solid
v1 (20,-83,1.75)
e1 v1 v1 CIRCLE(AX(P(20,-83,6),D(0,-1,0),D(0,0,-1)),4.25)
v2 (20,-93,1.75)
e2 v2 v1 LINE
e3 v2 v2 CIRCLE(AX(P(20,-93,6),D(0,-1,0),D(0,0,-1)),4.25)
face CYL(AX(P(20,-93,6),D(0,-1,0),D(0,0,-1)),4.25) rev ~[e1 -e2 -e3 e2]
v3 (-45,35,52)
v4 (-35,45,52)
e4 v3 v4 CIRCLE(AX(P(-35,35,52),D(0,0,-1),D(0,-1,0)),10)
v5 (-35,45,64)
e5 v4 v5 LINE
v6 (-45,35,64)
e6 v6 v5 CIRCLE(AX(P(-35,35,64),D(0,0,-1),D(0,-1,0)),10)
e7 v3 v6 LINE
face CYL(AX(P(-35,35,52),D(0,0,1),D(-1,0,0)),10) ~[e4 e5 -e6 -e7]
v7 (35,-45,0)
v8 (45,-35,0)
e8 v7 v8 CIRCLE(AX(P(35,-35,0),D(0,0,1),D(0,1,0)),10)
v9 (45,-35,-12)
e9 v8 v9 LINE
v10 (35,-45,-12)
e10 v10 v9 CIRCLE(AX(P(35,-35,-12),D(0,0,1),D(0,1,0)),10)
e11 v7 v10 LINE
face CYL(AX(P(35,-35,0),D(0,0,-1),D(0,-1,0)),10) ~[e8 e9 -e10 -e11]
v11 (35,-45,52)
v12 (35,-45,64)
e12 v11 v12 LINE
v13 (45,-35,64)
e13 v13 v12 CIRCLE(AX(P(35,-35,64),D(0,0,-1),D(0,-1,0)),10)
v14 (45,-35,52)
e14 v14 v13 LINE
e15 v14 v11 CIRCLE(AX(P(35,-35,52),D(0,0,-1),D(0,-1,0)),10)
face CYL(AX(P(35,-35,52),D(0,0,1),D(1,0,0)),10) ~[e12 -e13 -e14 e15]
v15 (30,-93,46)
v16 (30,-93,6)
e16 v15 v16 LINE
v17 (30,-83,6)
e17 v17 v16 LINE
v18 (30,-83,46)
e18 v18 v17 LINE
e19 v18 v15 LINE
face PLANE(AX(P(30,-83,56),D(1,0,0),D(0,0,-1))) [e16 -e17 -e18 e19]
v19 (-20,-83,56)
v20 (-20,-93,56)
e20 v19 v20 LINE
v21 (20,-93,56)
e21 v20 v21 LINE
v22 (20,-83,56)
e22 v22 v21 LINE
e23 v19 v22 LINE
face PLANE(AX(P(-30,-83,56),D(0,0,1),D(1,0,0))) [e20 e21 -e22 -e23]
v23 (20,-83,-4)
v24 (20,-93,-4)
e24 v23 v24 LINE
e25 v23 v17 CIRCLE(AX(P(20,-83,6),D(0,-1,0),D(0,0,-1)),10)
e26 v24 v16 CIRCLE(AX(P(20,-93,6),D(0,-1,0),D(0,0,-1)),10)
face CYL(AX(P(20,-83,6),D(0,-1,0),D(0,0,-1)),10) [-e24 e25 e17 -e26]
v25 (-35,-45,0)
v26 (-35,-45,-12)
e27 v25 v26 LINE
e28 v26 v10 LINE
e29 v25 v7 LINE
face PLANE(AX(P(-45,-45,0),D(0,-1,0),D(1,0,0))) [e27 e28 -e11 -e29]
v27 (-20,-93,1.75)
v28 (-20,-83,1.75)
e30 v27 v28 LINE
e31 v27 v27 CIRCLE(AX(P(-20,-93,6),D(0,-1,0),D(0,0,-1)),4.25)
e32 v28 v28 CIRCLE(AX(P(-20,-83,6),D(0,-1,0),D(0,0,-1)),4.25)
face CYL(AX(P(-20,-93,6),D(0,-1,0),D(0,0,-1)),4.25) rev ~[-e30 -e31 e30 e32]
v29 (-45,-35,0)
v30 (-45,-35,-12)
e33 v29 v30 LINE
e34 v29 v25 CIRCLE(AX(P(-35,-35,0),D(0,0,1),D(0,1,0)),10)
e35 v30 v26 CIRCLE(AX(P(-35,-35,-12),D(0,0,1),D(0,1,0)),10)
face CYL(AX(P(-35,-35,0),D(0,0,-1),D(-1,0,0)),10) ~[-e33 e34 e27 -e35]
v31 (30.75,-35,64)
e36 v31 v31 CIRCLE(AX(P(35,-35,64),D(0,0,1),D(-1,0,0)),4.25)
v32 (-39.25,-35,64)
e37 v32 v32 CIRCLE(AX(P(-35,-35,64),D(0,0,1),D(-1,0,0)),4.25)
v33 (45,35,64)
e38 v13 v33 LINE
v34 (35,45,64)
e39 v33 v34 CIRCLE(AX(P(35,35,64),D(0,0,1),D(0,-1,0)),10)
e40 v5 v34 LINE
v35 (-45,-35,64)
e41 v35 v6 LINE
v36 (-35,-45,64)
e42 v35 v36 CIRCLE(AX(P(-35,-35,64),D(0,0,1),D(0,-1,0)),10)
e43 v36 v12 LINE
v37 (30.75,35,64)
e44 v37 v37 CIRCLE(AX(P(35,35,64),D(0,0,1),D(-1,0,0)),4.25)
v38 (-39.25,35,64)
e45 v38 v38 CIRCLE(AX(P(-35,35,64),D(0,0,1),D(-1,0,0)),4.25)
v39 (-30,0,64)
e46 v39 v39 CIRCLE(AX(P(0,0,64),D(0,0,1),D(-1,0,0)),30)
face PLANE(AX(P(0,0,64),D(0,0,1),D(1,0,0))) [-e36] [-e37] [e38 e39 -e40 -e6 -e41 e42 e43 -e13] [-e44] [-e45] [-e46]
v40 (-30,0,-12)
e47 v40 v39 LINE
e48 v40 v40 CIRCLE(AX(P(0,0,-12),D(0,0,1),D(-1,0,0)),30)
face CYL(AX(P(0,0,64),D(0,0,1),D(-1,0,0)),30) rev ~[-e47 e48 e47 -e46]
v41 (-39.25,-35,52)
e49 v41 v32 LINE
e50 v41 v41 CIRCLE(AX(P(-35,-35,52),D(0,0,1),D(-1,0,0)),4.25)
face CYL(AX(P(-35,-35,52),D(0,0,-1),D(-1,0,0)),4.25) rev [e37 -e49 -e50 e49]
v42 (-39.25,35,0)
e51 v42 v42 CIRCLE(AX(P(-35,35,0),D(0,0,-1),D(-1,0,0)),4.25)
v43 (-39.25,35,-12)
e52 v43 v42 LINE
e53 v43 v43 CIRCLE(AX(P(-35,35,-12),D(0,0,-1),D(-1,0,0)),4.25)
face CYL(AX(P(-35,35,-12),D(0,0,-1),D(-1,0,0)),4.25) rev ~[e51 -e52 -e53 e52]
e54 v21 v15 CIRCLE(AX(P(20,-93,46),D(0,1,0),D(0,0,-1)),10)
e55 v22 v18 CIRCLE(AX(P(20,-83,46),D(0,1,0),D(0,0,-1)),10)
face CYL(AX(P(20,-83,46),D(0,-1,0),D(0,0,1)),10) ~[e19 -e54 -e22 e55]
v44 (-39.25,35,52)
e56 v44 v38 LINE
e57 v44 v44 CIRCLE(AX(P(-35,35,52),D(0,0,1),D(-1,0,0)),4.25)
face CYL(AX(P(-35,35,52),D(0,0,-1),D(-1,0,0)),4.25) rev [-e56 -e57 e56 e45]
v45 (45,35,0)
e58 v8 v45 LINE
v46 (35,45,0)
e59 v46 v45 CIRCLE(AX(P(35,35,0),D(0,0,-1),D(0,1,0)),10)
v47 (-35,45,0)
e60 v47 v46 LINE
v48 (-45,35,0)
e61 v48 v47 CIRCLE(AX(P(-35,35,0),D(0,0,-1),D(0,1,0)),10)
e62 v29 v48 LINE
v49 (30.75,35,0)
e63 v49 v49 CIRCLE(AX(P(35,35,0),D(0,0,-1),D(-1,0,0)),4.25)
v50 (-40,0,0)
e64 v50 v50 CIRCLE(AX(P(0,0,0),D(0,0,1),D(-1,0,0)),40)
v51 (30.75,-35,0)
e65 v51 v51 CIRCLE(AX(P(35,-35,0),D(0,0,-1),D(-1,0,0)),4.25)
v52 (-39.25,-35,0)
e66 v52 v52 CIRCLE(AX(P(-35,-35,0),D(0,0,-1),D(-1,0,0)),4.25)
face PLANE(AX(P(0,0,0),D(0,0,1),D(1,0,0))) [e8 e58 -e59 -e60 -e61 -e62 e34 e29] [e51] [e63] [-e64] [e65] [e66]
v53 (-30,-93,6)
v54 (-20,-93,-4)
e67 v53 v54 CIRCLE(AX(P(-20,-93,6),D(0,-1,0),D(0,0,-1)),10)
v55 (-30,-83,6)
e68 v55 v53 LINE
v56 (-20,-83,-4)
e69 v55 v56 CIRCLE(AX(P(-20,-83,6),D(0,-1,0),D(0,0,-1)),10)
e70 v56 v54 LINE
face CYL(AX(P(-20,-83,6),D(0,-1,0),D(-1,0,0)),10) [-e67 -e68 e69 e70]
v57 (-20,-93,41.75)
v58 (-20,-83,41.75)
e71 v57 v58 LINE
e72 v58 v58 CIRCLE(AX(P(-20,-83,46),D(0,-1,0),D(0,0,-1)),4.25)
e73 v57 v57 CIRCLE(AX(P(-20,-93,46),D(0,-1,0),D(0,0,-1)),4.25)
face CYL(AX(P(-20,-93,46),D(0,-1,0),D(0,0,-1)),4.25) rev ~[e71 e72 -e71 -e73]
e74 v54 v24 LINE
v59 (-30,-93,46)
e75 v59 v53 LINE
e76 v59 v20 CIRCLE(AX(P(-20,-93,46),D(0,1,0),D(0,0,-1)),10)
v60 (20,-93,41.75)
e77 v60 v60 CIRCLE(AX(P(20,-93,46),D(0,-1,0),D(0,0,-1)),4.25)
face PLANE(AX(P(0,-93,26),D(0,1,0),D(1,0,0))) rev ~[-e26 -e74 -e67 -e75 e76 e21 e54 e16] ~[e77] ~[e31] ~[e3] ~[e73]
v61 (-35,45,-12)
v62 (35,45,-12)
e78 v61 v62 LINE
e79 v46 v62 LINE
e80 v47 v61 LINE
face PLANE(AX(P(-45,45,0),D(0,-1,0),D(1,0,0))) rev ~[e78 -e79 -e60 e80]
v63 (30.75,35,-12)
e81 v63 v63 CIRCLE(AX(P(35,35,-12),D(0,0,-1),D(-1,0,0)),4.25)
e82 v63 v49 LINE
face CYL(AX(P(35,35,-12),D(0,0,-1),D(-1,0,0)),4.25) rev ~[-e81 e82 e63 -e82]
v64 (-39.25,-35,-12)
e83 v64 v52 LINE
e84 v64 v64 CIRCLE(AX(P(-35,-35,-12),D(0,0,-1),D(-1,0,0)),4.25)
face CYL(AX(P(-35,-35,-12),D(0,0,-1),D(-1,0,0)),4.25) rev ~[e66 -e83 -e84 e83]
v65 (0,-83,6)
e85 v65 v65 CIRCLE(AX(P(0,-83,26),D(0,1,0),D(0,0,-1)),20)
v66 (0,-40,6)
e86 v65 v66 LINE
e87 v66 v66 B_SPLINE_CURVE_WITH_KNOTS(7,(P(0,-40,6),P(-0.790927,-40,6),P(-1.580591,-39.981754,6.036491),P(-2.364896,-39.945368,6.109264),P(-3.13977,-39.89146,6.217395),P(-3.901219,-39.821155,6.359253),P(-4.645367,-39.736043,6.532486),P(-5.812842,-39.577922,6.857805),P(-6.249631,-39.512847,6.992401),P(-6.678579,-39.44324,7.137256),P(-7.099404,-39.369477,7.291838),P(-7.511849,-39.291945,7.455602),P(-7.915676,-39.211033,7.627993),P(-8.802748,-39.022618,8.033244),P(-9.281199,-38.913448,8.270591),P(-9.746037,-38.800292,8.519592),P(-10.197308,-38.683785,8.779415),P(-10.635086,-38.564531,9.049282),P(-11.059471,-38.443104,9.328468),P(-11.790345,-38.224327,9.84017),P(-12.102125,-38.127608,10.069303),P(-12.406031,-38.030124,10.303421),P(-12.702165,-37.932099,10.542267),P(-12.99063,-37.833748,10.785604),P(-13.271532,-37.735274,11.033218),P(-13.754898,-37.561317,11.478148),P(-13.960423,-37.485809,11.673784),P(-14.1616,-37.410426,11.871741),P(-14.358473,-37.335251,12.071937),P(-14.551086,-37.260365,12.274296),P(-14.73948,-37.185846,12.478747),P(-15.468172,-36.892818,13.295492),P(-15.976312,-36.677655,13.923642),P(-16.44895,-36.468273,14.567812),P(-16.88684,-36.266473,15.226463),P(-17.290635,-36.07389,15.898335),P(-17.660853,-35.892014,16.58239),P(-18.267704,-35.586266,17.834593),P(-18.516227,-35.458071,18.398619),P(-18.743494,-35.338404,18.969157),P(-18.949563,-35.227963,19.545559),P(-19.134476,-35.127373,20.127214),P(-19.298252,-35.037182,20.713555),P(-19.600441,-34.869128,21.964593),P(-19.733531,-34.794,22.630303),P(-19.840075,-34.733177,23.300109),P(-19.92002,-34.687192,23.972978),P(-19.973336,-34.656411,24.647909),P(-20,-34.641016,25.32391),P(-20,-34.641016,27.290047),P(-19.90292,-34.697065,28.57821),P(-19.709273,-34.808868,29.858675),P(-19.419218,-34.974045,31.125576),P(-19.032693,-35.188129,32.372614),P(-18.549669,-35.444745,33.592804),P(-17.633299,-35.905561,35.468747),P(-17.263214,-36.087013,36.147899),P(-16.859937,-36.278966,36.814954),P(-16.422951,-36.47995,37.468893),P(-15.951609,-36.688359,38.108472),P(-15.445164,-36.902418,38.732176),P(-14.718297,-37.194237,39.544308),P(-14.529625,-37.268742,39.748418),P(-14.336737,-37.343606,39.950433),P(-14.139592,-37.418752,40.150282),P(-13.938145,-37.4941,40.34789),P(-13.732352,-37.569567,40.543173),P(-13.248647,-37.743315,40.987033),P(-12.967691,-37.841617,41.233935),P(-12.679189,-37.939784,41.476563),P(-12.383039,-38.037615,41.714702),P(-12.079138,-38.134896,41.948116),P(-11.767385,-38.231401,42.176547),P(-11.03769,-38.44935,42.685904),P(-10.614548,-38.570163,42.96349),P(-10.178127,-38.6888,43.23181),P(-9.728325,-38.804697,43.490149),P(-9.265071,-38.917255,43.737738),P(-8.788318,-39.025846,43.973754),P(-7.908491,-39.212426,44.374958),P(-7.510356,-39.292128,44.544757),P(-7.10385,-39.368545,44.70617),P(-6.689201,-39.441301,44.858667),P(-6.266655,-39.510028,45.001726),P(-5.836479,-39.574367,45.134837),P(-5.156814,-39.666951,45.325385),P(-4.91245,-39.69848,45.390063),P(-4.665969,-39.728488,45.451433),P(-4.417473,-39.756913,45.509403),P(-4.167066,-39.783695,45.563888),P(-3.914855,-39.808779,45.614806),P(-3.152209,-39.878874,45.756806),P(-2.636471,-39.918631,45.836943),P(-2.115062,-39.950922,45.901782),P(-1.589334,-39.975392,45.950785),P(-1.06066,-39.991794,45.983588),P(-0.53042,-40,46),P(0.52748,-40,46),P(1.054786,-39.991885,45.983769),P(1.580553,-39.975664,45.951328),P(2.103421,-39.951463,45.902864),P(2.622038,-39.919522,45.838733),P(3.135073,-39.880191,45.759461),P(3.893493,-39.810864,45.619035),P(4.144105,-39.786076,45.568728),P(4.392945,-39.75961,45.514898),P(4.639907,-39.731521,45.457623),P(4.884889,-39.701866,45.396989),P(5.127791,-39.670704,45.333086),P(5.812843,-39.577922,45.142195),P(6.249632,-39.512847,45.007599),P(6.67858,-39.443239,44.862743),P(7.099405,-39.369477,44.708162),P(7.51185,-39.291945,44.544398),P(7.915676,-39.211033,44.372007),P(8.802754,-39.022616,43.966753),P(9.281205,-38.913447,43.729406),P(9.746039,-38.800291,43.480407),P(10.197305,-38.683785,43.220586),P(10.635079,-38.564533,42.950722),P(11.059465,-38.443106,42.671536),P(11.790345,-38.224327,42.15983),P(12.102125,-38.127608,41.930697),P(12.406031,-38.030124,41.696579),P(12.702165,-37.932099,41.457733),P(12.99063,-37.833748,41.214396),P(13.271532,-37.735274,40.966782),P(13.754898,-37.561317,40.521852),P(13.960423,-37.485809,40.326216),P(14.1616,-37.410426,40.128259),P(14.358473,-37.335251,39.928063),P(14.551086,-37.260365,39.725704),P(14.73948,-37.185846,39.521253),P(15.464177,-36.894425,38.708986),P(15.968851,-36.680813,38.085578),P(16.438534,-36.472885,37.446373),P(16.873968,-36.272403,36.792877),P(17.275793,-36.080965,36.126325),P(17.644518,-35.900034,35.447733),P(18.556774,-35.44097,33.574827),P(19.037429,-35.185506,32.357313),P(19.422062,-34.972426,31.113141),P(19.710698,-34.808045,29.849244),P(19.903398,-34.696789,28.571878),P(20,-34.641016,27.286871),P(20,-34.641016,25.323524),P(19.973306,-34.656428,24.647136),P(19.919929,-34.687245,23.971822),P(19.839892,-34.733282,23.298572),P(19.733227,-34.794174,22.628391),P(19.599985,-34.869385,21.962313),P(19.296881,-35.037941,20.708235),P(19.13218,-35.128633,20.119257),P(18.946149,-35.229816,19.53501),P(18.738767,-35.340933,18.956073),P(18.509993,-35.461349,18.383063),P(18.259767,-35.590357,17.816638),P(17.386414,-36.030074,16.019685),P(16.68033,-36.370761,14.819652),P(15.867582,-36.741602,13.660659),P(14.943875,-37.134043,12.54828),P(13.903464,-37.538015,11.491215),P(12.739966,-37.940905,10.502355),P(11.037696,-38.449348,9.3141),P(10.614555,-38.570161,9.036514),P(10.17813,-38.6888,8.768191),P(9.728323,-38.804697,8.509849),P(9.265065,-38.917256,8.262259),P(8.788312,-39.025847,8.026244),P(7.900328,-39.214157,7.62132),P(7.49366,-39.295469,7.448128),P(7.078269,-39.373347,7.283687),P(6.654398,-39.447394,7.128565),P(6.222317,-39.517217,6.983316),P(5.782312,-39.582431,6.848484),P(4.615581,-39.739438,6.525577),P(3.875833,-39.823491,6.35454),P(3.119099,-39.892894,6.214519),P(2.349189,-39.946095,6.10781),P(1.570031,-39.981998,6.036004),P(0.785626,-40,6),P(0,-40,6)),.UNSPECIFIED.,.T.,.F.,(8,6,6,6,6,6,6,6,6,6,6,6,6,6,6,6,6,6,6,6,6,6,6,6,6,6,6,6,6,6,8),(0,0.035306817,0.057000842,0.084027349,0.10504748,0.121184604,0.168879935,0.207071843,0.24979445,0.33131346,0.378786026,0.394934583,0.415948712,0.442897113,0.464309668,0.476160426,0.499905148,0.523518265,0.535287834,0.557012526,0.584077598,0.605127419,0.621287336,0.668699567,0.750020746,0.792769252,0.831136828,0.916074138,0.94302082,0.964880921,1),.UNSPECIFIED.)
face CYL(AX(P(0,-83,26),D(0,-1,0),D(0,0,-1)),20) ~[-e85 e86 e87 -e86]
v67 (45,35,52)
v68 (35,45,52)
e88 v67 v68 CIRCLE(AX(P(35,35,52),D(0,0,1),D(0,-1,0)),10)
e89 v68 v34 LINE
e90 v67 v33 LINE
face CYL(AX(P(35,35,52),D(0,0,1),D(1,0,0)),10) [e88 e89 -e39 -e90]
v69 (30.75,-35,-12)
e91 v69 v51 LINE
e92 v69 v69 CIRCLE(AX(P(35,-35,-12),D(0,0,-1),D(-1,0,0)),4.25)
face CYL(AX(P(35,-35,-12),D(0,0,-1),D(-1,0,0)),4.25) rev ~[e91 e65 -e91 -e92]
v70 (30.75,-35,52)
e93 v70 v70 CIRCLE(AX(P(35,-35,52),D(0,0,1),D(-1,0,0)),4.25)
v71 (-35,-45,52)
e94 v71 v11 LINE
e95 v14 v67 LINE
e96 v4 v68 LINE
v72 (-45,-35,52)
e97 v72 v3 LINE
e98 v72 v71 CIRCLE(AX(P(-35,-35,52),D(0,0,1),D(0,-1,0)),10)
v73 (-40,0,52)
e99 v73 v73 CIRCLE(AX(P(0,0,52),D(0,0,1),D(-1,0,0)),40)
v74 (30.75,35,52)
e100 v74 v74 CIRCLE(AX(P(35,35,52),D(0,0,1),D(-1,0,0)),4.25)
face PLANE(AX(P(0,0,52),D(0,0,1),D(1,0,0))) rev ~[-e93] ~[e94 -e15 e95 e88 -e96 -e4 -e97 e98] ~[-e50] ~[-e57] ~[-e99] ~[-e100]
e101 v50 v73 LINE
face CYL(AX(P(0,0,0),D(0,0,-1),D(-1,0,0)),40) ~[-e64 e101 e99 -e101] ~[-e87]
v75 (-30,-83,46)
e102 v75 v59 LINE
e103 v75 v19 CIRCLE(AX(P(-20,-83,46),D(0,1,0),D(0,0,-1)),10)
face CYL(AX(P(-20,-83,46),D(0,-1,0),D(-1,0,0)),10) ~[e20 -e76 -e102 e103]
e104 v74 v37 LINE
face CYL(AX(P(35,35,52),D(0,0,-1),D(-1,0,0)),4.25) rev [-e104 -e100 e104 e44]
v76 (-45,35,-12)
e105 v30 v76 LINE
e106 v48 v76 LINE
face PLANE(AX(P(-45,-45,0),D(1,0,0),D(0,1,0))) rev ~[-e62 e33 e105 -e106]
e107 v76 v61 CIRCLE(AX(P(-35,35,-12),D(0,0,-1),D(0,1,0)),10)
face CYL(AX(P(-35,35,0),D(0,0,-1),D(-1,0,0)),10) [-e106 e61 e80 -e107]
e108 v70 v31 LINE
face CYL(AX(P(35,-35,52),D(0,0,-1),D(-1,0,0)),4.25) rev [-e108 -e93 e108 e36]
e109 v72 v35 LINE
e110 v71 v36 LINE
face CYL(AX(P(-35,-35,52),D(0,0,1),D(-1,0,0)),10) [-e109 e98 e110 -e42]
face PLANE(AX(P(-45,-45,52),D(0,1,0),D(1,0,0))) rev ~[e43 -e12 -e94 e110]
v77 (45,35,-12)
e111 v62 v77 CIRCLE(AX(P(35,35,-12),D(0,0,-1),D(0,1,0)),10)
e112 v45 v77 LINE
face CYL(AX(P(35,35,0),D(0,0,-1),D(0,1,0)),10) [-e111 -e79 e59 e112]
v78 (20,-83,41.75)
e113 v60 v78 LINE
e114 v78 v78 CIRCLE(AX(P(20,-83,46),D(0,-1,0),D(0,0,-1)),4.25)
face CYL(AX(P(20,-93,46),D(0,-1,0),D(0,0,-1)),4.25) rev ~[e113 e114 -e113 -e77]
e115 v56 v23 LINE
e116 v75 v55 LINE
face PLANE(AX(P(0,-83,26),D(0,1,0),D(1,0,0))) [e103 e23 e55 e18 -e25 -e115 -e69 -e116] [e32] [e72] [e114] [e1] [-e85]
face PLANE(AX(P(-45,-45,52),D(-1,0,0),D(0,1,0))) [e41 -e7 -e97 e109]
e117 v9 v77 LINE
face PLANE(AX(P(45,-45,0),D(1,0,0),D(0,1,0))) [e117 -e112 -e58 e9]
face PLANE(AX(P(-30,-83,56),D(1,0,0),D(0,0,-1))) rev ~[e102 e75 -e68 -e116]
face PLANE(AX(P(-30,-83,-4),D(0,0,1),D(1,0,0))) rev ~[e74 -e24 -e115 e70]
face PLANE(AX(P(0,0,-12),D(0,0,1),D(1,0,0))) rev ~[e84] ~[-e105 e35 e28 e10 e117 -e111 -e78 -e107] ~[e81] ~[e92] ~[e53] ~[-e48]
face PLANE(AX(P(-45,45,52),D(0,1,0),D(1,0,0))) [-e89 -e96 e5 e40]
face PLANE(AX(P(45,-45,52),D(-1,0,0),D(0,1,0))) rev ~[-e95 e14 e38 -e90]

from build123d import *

# Parameters (mm, degrees)
BODY_TUBE_SKETCH_R                 = 40
BODY_TUBE_SKETCH_R_2               = 30
BODY_TUBE_80_DEPTH                 = 52
INLET_FLANGE_SKETCH_W              = 90
INLET_FLANGE_SKETCH_H              = 90
INLET_FLANGE_90X90_DEPTH           = 12
OUTLET_FLANGE_SKETCH_W             = 90
OUTLET_FLANGE_SKETCH_H             = 90
OUTLET_FLANGE_90X90_DEPTH          = 12
FLANGE_BORE_SKETCH_R               = 30
FLANGE_BORE_60_DEPTH               = 100.126182212
OUTLET_FLANGE_CORNER_FILLETS_R10_R = 10
INLET_FLANGE_CORNER_FILLETS_R10_R  = 10
INLET_FLANGE_HOLES_SKETCH_R        = 4.25
INLET_FLANGE_HOLES_4X_8_5_DEPTH    = 12
OUTLET_START                       = -12
OUTLET_FLANGE_HOLES_SKETCH_R       = 4.25
OUTLET_FLANGE_HOLES_4X_8_5_DEPTH   = 12
BRANCH_PIPE_SKETCH_R               = 20
BRANCH_PIPE_40_DEPTH               = 50
MOUNTING_FOOT_SKETCH_W             = 60
MOUNTING_FOOT_SKETCH_H             = 60
MOUNTING_FOOT_60X60_DEPTH          = 10
MOUNTING_FOOT_CORNER_FILLETS_R10_R = 10
MOUNTING_FOOT_HOLES_SKETCH_R       = 4.25
MOUNTING_FOOT_HOLES_4X_8_5_DEPTH   = 10


with BuildPart() as part:
    # Body Tube Sketch → Body Tube Ø80 (new body)
    with BuildSketch(Plane.XY):
        with Locations(Location((0, 0, 0), (0, 0, 180))):
            Circle(BODY_TUBE_SKETCH_R)
        with Locations(Location((0, 0, 0), (0, 0, 180))):
            Circle(BODY_TUBE_SKETCH_R_2, mode=Mode.SUBTRACT)
    extrude(amount=BODY_TUBE_80_DEPTH)

    # Inlet Flange Sketch → Inlet Flange 90x90 (add)
    with BuildSketch(Plane.XY):
        Rectangle(INLET_FLANGE_SKETCH_W, INLET_FLANGE_SKETCH_H)
    extrude(amount=-INLET_FLANGE_90X90_DEPTH)

    # Outlet Flange Sketch → Outlet Flange 90x90 (add)
    with BuildSketch(Plane.XY.offset(52)):
        Rectangle(OUTLET_FLANGE_SKETCH_W, OUTLET_FLANGE_SKETCH_H)
    extrude(amount=OUTLET_FLANGE_90X90_DEPTH)

    # Flange Bore Sketch → Flange Bore Ø60 (cut, through all)
    with BuildSketch(Plane.XY.offset(64)):
        with Locations(Location((0, 0, 0), (0, 0, 180))):
            Circle(FLANGE_BORE_SKETCH_R)
    extrude(amount=-FLANGE_BORE_60_DEPTH, mode=Mode.SUBTRACT)

    # Outlet Flange Corner Fillets R10
    outlet_flange_corner_fillets_r10_edges = [part.edges().sort_by_distance(p)[0] for p in [
        (45, -45, 58),
        (45, 45, 58),
        (-45, 45, 58),
        (-45, -45, 58),
    ]]
    fillet(outlet_flange_corner_fillets_r10_edges, radius=OUTLET_FLANGE_CORNER_FILLETS_R10_R)

    # Inlet Flange Corner Fillets R10
    inlet_flange_corner_fillets_r10_edges = [part.edges().sort_by_distance(p)[0] for p in [
        (-45, -45, -6),
        (-45, 45, -6),
        (45, 45, -6),
        (45, -45, -6),
    ]]
    fillet(inlet_flange_corner_fillets_r10_edges, radius=INLET_FLANGE_CORNER_FILLETS_R10_R)

    # Inlet Flange Holes Sketch → Inlet Flange Holes 4xØ8.5 (cut)
    with BuildSketch(Plane(origin=(0, 0, -12), x_dir=(-1, 0, 0), z_dir=(0, 0, -1))):
        with Locations((-35, 35)):
            Circle(INLET_FLANGE_HOLES_SKETCH_R)
        with Locations((35, 35)):
            Circle(INLET_FLANGE_HOLES_SKETCH_R)
        with Locations((35, -35)):
            Circle(INLET_FLANGE_HOLES_SKETCH_R)
        with Locations((-35, -35)):
            Circle(INLET_FLANGE_HOLES_SKETCH_R)
    extrude(amount=-INLET_FLANGE_HOLES_4X_8_5_DEPTH, mode=Mode.SUBTRACT)

    # Outlet Flange Holes Sketch → Outlet Flange Holes 4xØ8.5 (cut)
    with BuildSketch(Plane.XY.offset(64).offset(OUTLET_START)):
        with Locations(Location((-35, 35, 0), (0, 0, 180))):
            Circle(OUTLET_FLANGE_HOLES_SKETCH_R)
        with Locations(Location((35, 35, 0), (0, 0, 180))):
            Circle(OUTLET_FLANGE_HOLES_SKETCH_R)
        with Locations(Location((35, -35, 0), (0, 0, 180))):
            Circle(OUTLET_FLANGE_HOLES_SKETCH_R)
        with Locations(Location((-35, -35, 0), (0, 0, 180))):
            Circle(OUTLET_FLANGE_HOLES_SKETCH_R)
    extrude(amount=OUTLET_FLANGE_HOLES_4X_8_5_DEPTH, mode=Mode.SUBTRACT)

    # Branch Pipe Sketch → Branch Pipe Ø40 (add)
    with BuildSketch(Plane(origin=(0, -83, 0), x_dir=(1, 0, 0), z_dir=(0, 1, 0))):
        with Locations(Location((0, -26, 0), (0, 0, 90))):
            Circle(BRANCH_PIPE_SKETCH_R)
    extrude(amount=BRANCH_PIPE_40_DEPTH)

    # Mounting Foot Sketch → Mounting Foot 60x60 (add)
    with BuildSketch(Plane(origin=(0, -83, 0), x_dir=(1, 0, 0), z_dir=(0, 1, 0))):
        with Locations((0, -26)):
            Rectangle(MOUNTING_FOOT_SKETCH_W, MOUNTING_FOOT_SKETCH_H)
    extrude(amount=-MOUNTING_FOOT_60X60_DEPTH)

    # Mounting Foot Corner Fillets R10
    mounting_foot_corner_fillets_r10_edges = [part.edges().sort_by_distance(p)[0] for p in [
        (30, -88, -4),
        (30, -88, 56),
        (-30, -88, 56),
        (-30, -88, -4),
    ]]
    fillet(mounting_foot_corner_fillets_r10_edges, radius=MOUNTING_FOOT_CORNER_FILLETS_R10_R)

    # Mounting Foot Holes Sketch → Mounting Foot Holes 4xØ8.5 (cut)
    with BuildSketch(Plane.XZ.offset(93)):
        with Locations(Location((-20, 46, 0), (0, 0, 270))):
            Circle(MOUNTING_FOOT_HOLES_SKETCH_R)
        with Locations(Location((20, 46, 0), (0, 0, 270))):
            Circle(MOUNTING_FOOT_HOLES_SKETCH_R)
        with Locations(Location((20, 6, 0), (0, 0, 270))):
            Circle(MOUNTING_FOOT_HOLES_SKETCH_R)
        with Locations(Location((-20, 6, 0), (0, 0, 270))):
            Circle(MOUNTING_FOOT_HOLES_SKETCH_R)
    extrude(amount=-MOUNTING_FOOT_HOLES_4X_8_5_DEPTH, mode=Mode.SUBTRACT)


solid = part.part
